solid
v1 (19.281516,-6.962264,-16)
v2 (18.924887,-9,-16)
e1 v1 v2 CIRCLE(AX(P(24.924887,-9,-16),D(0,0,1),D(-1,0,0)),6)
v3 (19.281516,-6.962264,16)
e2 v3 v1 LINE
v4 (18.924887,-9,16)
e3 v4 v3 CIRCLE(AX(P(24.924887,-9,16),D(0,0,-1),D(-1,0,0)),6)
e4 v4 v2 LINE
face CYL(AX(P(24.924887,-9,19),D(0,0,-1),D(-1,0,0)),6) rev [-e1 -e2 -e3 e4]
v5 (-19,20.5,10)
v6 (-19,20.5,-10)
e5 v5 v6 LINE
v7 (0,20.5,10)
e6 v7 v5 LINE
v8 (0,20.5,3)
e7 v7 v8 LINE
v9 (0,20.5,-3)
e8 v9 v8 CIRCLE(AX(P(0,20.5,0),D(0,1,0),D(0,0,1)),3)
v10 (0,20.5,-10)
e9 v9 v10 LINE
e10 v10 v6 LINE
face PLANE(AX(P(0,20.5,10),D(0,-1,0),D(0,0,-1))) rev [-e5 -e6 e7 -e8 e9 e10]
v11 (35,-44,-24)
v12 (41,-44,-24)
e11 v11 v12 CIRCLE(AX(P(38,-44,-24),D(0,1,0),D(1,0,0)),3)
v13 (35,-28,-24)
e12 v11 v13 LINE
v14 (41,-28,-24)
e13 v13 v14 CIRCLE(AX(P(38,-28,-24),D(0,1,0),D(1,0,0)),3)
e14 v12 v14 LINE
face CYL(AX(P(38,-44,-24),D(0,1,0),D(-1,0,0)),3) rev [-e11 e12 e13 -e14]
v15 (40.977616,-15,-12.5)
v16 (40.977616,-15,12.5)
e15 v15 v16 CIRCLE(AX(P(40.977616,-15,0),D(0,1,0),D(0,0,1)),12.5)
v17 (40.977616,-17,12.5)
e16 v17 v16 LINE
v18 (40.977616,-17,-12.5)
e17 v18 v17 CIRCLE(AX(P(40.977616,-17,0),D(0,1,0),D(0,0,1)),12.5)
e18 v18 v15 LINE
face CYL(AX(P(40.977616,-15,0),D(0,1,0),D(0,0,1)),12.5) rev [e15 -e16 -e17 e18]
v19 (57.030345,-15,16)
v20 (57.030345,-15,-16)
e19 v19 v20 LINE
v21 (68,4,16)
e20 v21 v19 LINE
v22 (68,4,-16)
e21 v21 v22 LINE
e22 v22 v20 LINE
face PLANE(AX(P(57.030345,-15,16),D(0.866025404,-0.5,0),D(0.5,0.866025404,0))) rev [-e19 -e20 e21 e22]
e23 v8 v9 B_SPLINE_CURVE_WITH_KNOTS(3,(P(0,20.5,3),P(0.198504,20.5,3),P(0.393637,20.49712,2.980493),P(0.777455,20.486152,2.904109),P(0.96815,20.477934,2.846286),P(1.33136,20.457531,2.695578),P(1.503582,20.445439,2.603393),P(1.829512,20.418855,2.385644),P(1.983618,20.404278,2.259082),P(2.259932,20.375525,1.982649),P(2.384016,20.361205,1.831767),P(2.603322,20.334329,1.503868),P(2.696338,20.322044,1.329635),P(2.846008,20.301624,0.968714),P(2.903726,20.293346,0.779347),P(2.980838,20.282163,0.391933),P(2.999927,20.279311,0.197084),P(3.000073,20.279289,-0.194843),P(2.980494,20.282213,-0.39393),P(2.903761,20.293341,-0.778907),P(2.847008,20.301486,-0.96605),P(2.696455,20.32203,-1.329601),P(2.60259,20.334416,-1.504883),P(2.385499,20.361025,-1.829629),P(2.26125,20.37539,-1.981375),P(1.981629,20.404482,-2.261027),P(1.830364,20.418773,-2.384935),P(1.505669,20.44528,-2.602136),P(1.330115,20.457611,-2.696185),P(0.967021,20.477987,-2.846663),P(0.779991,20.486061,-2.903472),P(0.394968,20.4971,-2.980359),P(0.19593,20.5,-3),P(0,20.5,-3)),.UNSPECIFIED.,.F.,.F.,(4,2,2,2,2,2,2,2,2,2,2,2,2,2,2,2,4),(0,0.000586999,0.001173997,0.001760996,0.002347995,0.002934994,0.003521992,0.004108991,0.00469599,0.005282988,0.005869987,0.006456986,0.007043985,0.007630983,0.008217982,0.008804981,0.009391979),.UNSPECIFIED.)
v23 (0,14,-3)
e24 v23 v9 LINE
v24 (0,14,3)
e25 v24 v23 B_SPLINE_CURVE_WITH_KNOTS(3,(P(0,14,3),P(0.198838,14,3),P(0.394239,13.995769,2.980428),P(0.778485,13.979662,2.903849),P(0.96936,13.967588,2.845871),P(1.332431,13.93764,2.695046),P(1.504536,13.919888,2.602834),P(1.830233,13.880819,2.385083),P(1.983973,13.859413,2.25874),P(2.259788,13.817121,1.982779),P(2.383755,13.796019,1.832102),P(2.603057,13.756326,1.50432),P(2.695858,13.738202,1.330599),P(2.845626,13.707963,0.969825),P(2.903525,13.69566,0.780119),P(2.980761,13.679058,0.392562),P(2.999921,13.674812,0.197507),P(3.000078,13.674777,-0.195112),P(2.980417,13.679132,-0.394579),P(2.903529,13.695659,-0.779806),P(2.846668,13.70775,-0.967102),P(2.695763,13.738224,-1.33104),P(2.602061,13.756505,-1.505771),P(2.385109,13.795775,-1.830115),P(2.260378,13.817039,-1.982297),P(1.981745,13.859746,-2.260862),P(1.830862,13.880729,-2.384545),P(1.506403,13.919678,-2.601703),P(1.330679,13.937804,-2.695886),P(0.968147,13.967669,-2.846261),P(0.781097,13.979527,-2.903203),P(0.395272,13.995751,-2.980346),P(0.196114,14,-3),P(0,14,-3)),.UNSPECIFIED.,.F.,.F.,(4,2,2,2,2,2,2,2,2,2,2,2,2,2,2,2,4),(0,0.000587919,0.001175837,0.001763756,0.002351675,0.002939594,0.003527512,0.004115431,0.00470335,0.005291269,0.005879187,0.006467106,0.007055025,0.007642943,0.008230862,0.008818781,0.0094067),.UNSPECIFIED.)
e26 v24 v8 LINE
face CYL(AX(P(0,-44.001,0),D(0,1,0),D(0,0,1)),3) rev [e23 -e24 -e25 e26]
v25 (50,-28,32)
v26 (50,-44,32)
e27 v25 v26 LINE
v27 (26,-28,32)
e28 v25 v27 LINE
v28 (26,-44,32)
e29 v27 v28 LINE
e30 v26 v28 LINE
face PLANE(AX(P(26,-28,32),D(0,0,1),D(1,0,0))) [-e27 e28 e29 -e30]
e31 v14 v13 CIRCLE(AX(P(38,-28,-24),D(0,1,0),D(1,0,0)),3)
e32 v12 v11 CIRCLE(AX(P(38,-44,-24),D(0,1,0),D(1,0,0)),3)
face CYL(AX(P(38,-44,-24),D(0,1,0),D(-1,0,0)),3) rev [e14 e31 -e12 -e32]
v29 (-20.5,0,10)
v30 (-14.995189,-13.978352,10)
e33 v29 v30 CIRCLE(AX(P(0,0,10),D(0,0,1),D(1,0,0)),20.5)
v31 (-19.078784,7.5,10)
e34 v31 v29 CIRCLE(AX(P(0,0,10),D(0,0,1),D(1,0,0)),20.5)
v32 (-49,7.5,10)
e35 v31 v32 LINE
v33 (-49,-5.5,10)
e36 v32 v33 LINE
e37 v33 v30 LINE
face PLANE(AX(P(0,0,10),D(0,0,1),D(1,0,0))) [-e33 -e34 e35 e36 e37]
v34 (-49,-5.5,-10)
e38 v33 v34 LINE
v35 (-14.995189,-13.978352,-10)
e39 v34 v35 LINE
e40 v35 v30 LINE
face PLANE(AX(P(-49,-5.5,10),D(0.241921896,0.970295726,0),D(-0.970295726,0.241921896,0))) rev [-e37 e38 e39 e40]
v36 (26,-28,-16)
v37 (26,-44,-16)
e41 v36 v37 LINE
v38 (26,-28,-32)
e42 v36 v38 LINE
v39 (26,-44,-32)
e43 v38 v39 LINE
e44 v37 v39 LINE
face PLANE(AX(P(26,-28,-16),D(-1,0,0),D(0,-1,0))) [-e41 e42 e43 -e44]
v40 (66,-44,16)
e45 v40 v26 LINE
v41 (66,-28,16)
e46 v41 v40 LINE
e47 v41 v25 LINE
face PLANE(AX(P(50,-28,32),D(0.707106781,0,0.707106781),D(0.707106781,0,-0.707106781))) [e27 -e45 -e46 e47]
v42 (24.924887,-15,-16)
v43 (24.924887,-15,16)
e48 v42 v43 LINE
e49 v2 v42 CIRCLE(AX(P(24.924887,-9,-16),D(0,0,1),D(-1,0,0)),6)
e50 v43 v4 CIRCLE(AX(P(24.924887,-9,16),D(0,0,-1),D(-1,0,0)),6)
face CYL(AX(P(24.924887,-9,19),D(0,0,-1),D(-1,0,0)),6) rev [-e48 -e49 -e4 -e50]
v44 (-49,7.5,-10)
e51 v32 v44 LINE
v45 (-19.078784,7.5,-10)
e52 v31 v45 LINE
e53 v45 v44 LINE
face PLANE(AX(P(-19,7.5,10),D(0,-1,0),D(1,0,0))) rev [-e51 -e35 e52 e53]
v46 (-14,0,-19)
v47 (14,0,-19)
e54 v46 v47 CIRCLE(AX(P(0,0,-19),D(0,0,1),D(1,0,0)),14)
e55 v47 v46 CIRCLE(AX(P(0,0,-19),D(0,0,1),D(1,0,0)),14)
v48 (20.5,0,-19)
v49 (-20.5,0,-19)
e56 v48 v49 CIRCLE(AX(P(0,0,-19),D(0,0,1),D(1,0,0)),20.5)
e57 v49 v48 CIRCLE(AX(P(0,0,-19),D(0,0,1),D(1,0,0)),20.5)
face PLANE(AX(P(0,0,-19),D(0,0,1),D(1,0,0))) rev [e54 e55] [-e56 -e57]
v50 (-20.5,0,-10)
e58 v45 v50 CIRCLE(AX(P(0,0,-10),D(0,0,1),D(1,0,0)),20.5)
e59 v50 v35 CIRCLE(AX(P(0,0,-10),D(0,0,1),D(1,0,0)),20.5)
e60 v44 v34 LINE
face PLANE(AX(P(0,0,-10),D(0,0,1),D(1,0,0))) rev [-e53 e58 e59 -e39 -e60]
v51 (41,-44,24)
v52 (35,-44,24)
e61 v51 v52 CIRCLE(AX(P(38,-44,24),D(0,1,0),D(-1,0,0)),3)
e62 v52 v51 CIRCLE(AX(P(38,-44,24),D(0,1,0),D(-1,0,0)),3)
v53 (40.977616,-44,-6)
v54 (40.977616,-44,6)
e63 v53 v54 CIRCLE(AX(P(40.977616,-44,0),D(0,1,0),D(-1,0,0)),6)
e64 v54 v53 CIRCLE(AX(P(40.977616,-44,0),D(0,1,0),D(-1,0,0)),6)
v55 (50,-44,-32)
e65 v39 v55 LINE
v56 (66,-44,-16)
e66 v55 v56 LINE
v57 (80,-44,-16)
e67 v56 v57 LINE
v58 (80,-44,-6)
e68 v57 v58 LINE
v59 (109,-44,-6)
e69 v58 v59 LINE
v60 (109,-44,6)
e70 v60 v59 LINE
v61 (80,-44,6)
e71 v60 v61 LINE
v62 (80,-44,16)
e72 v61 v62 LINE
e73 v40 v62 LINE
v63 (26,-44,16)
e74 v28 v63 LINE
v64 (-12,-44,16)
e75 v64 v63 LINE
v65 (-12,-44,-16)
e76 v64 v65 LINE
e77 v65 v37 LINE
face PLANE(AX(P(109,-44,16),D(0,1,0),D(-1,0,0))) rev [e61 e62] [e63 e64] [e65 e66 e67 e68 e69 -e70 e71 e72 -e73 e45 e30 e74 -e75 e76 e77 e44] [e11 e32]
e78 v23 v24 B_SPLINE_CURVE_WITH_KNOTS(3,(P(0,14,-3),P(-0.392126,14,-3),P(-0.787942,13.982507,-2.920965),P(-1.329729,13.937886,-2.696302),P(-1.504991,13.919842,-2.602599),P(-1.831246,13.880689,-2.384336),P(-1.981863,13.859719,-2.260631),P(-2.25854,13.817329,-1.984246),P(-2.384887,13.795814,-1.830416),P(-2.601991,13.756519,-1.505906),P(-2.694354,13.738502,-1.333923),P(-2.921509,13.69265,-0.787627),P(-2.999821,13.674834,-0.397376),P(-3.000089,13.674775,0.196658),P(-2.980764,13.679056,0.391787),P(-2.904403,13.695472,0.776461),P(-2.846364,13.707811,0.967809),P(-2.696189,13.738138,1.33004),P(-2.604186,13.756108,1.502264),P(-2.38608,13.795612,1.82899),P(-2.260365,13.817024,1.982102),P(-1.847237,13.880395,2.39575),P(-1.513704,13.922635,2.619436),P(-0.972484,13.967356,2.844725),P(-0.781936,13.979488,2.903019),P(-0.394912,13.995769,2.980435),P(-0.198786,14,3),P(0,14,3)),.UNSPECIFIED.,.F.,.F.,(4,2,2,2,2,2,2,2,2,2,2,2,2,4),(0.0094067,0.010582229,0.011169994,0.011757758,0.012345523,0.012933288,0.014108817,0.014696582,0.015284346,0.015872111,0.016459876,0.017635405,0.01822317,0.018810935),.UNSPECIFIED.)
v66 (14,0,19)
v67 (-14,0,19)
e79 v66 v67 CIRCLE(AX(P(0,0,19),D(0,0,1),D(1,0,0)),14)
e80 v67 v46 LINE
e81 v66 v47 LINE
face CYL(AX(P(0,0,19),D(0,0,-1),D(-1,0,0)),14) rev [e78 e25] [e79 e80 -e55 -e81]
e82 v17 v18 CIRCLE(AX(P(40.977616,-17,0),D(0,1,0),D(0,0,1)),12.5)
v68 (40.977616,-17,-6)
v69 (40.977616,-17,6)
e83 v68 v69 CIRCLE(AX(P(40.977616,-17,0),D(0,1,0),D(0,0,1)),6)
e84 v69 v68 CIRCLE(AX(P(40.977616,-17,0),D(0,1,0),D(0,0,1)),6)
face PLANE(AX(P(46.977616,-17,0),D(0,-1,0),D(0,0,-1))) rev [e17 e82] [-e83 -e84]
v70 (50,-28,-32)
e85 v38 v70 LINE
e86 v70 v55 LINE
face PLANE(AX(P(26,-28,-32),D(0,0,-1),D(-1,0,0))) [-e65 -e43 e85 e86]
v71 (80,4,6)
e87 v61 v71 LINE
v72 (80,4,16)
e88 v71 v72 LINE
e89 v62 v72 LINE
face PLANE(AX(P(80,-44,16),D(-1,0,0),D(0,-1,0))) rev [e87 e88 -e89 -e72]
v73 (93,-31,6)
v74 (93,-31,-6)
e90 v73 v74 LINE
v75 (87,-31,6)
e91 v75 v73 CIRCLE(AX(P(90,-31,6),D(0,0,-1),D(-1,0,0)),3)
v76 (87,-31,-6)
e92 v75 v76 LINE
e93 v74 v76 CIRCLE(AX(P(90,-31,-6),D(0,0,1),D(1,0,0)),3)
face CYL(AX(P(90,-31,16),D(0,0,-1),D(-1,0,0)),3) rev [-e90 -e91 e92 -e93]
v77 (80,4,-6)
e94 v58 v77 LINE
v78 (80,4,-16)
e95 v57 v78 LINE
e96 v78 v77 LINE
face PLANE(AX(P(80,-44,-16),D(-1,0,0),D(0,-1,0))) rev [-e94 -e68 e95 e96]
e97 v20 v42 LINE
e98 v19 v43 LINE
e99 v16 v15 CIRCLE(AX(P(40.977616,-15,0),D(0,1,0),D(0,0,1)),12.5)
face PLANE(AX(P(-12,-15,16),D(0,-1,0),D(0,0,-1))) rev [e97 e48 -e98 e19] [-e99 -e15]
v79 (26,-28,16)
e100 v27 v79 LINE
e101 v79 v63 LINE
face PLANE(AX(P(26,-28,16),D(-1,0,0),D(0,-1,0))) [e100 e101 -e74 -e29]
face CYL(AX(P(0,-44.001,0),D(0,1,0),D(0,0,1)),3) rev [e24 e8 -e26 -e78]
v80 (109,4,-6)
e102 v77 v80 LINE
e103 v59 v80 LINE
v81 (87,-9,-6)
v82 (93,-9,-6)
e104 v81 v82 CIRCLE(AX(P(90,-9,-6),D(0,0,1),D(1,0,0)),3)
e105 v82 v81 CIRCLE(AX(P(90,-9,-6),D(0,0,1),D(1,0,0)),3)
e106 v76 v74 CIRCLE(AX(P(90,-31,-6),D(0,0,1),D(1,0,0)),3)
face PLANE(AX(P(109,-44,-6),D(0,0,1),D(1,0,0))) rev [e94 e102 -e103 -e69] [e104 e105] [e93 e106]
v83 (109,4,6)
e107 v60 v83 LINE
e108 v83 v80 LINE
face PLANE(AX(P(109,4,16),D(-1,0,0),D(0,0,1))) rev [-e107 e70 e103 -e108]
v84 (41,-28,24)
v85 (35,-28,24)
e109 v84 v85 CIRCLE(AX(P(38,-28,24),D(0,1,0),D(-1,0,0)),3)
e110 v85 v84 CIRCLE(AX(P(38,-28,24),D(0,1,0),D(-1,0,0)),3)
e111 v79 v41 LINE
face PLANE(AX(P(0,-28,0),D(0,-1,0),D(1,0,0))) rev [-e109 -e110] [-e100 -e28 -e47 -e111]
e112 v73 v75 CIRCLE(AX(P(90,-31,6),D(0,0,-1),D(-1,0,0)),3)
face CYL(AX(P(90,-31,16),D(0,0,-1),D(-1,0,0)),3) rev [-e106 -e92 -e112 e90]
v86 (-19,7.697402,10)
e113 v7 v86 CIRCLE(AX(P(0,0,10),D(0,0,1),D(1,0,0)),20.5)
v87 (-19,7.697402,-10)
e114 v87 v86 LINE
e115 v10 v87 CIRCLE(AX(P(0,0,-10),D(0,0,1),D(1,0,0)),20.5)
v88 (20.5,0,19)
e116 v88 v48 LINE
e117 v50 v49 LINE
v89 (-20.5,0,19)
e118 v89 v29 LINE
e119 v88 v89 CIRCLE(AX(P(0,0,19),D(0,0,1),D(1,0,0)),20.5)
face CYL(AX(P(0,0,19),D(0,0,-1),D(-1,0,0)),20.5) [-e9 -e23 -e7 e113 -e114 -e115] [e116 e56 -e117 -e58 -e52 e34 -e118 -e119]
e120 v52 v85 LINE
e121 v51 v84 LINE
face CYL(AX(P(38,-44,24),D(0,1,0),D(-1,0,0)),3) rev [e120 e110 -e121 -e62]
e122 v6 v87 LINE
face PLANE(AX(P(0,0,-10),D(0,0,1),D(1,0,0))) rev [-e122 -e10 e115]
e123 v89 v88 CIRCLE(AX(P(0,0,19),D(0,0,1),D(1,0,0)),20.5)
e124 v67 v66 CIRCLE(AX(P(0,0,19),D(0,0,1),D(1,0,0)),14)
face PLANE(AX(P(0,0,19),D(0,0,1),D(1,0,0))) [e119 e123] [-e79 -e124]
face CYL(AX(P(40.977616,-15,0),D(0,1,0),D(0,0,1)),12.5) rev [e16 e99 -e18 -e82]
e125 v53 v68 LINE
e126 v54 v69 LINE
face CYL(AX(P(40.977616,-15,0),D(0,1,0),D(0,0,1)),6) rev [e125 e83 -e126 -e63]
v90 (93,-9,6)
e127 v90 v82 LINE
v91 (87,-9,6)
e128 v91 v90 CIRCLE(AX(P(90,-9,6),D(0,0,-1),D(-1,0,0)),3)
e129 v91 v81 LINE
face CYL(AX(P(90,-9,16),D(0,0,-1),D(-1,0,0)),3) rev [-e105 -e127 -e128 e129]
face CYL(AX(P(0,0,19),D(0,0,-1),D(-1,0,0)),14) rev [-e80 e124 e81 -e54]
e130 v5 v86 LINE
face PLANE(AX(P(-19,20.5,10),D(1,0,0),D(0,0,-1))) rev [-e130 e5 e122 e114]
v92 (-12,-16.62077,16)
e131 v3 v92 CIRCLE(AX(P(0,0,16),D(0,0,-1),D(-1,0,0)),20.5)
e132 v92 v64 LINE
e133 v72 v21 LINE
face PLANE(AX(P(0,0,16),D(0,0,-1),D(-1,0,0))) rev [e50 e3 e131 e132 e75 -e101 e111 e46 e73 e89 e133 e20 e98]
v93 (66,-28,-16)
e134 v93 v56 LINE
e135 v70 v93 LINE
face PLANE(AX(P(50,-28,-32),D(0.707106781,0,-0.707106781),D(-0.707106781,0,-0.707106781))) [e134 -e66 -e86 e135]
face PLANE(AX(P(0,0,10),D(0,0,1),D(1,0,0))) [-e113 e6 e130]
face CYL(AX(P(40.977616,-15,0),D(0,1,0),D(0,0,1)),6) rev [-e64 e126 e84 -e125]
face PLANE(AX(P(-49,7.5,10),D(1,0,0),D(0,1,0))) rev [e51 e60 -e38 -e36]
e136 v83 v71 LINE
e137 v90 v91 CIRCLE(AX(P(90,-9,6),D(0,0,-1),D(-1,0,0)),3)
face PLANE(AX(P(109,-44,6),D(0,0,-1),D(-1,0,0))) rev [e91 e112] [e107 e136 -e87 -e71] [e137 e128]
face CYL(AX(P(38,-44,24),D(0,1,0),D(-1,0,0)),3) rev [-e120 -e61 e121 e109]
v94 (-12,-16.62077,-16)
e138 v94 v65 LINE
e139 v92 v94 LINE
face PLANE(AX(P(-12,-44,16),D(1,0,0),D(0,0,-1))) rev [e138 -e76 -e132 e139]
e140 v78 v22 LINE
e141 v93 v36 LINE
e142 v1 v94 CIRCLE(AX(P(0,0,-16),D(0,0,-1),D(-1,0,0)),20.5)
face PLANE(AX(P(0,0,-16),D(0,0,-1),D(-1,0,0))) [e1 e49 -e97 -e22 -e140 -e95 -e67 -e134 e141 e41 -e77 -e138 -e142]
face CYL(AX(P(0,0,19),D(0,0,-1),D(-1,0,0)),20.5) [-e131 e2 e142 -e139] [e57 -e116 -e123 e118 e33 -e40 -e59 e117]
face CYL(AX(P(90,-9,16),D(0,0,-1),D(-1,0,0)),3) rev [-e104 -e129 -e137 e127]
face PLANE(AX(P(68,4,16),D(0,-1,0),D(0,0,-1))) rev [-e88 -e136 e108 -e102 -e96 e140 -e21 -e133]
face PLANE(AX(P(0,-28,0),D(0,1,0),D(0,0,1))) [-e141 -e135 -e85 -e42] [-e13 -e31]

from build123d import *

# Parameters (mm, degrees)
BASE_BLOCK_SKETCH_R              = 20.5
BASE_BLOCK_SKETCH_R_2            = 14
BASE_BLOCK_DEPTH                 = 19
JOURNAL_HOUSING_PROFILE_SKETCH_R = 3
JOURNAL_HOUSING_DEPTH            = 16
HOUSING_FILLET_R6_R              = 6
MOUNTING_FLANGE_DEPTH            = 16
HOUSING_CUT_SKETCH_W             = 29
HOUSING_CUT_SKETCH_H             = 10
HOUSING_CUT_DEPTH                = 124.324774478
FLANGE_HOLES_SKETCH_R            = 3
FLANGE_HOLES_2X_6_DEPTH          = 16
COUNTERBORED_HOLE_12_D           = 12
COUNTERBORED_HOLE_12_DEPTH       = 99.788526395
COUNTERBORED_HOLE_12_CBORE_D     = 25
COUNTERBORED_HOLE_12_CBORE_DEPTH = 2
SIDE_LUG_DEPTH                   = 10
LUG_HOLE_6_REACH                 = 132.634
LUG_HOLE_6_END_RADIUS            = 14
LUG_HOLE_SKETCH_R                = 3


with BuildPart() as part:
    # Base Block Sketch → Base Block (new, symmetric)
    with BuildSketch(Plane.XY):
        Circle(BASE_BLOCK_SKETCH_R)
        Circle(BASE_BLOCK_SKETCH_R_2, mode=Mode.SUBTRACT)
    extrude(amount=BASE_BLOCK_DEPTH, both=True)

    # Journal Housing Profile Sketch → Journal Housing (add, symmetric)
    with BuildSketch(Plane.XY):
        Polygon((-12, -44), (-12, -15), (57.030344885, -15), (68, 4), (109, 4), (109, -44), align=None)
        with Locations((90, -31)):
            Circle(JOURNAL_HOUSING_PROFILE_SKETCH_R, mode=Mode.SUBTRACT)
        with Locations((90, -9)):
            Circle(JOURNAL_HOUSING_PROFILE_SKETCH_R, mode=Mode.SUBTRACT)
    extrude(amount=JOURNAL_HOUSING_DEPTH, both=True)

    # Housing Fillet R6
    housing_fillet_r6_edges = [part.edges().sort_by_distance(p)[0] for p in [
        (13.973188612, -15, 0),
    ]]
    fillet(housing_fillet_r6_edges, radius=HOUSING_FILLET_R6_R)

    # Mounting Flange Sketch → Mounting Flange (add)
    with BuildSketch(Plane.XZ.offset(44)):
        Polygon((26, 16), (26, 32), (50, 32), (66, 16), align=None)
        Polygon((50, -32), (66, -16), (26, -16), (26, -32), align=None)
    extrude(amount=-MOUNTING_FLANGE_DEPTH)

    # Housing Cut Sketch → Housing Cut (cut, through all)
    with BuildSketch(Plane(origin=(0, 4, 0), x_dir=(1, 0, 0), z_dir=(0, 1, 0))):
        with Locations((94.5, -11)):
            Rectangle(HOUSING_CUT_SKETCH_W, HOUSING_CUT_SKETCH_H)
        with Locations((94.5, 11)):
            Rectangle(HOUSING_CUT_SKETCH_W, HOUSING_CUT_SKETCH_H)
    extrude(amount=-HOUSING_CUT_DEPTH, mode=Mode.SUBTRACT)

    # Flange Holes Sketch → Flange Holes 2xØ6 (cut)
    with BuildSketch(Plane(origin=(0, -28, 0), x_dir=(1, 0, 0), z_dir=(0, 1, 0))):
        with Locations(Location((38, -24, 0), (0, 0, 180))):
            Circle(FLANGE_HOLES_SKETCH_R)
        with Locations((38, 24)):
            Circle(FLANGE_HOLES_SKETCH_R)
    extrude(amount=-FLANGE_HOLES_2X_6_DEPTH, mode=Mode.SUBTRACT)

    # Counterbored Hole Ø12
    with Locations(Plane(origin=(40.977616023, -15, 0), x_dir=(0, 0, 1), z_dir=(0, 1, 0))):
        with Locations((0, 0)):
            CounterBoreHole(COUNTERBORED_HOLE_12_D / 2, COUNTERBORED_HOLE_12_CBORE_D / 2, COUNTERBORED_HOLE_12_CBORE_DEPTH, depth=COUNTERBORED_HOLE_12_DEPTH)

    # Side Lug Sketch → Side Lug (add, symmetric)
    with BuildSketch(Plane.XY):
        with BuildLine():
            Line((0, 20.5), (-19, 20.5))
            Line((-19, 20.5), (-19, 7.5))
            Line((-19, 7.5), (-49, 7.5))
            Line((-49, 7.5), (-49, -5.5))
            Line((-49, -5.5), (-13.090107344, -14.453341818))
            ThreePointArc((-13.090107344, -14.453341818), (-18.194644342, 7.014621677), (0, 19.5))
            Line((0, 19.5), (0, 20.5))
        make_face()
    extrude(amount=SIDE_LUG_DEPTH, both=True)

    # Lug Hole Ø6: up to this cylinder (the profile starts outside it)
    lug_hole_6_end = Plane(origin=(0, 0, 0), z_dir=(0, 0, -1)) * Cylinder(LUG_HOLE_6_END_RADIUS, 294.268, mode=Mode.PRIVATE)
    # Lug Hole Sketch → Lug Hole Ø6 (cut, up to the surface)
    with BuildSketch(Plane(origin=(0, 20.5, 0), x_dir=(1, 0, 0), z_dir=(0, 1, 0)), mode=Mode.PRIVATE) as lug_hole_6_sk1:
        with Locations(Location((0, 0, 0), (0, 0, 270))):
            Circle(LUG_HOLE_SKETCH_R)
    lug_hole_6_tool1 = extrude(lug_hole_6_sk1.sketch, amount=-LUG_HOLE_6_REACH, mode=Mode.PRIVATE) - lug_hole_6_end
    add(lug_hole_6_tool1.solids().sort_by_distance((0, 20.5, 0))[0], mode=Mode.SUBTRACT)


solid = part.part
